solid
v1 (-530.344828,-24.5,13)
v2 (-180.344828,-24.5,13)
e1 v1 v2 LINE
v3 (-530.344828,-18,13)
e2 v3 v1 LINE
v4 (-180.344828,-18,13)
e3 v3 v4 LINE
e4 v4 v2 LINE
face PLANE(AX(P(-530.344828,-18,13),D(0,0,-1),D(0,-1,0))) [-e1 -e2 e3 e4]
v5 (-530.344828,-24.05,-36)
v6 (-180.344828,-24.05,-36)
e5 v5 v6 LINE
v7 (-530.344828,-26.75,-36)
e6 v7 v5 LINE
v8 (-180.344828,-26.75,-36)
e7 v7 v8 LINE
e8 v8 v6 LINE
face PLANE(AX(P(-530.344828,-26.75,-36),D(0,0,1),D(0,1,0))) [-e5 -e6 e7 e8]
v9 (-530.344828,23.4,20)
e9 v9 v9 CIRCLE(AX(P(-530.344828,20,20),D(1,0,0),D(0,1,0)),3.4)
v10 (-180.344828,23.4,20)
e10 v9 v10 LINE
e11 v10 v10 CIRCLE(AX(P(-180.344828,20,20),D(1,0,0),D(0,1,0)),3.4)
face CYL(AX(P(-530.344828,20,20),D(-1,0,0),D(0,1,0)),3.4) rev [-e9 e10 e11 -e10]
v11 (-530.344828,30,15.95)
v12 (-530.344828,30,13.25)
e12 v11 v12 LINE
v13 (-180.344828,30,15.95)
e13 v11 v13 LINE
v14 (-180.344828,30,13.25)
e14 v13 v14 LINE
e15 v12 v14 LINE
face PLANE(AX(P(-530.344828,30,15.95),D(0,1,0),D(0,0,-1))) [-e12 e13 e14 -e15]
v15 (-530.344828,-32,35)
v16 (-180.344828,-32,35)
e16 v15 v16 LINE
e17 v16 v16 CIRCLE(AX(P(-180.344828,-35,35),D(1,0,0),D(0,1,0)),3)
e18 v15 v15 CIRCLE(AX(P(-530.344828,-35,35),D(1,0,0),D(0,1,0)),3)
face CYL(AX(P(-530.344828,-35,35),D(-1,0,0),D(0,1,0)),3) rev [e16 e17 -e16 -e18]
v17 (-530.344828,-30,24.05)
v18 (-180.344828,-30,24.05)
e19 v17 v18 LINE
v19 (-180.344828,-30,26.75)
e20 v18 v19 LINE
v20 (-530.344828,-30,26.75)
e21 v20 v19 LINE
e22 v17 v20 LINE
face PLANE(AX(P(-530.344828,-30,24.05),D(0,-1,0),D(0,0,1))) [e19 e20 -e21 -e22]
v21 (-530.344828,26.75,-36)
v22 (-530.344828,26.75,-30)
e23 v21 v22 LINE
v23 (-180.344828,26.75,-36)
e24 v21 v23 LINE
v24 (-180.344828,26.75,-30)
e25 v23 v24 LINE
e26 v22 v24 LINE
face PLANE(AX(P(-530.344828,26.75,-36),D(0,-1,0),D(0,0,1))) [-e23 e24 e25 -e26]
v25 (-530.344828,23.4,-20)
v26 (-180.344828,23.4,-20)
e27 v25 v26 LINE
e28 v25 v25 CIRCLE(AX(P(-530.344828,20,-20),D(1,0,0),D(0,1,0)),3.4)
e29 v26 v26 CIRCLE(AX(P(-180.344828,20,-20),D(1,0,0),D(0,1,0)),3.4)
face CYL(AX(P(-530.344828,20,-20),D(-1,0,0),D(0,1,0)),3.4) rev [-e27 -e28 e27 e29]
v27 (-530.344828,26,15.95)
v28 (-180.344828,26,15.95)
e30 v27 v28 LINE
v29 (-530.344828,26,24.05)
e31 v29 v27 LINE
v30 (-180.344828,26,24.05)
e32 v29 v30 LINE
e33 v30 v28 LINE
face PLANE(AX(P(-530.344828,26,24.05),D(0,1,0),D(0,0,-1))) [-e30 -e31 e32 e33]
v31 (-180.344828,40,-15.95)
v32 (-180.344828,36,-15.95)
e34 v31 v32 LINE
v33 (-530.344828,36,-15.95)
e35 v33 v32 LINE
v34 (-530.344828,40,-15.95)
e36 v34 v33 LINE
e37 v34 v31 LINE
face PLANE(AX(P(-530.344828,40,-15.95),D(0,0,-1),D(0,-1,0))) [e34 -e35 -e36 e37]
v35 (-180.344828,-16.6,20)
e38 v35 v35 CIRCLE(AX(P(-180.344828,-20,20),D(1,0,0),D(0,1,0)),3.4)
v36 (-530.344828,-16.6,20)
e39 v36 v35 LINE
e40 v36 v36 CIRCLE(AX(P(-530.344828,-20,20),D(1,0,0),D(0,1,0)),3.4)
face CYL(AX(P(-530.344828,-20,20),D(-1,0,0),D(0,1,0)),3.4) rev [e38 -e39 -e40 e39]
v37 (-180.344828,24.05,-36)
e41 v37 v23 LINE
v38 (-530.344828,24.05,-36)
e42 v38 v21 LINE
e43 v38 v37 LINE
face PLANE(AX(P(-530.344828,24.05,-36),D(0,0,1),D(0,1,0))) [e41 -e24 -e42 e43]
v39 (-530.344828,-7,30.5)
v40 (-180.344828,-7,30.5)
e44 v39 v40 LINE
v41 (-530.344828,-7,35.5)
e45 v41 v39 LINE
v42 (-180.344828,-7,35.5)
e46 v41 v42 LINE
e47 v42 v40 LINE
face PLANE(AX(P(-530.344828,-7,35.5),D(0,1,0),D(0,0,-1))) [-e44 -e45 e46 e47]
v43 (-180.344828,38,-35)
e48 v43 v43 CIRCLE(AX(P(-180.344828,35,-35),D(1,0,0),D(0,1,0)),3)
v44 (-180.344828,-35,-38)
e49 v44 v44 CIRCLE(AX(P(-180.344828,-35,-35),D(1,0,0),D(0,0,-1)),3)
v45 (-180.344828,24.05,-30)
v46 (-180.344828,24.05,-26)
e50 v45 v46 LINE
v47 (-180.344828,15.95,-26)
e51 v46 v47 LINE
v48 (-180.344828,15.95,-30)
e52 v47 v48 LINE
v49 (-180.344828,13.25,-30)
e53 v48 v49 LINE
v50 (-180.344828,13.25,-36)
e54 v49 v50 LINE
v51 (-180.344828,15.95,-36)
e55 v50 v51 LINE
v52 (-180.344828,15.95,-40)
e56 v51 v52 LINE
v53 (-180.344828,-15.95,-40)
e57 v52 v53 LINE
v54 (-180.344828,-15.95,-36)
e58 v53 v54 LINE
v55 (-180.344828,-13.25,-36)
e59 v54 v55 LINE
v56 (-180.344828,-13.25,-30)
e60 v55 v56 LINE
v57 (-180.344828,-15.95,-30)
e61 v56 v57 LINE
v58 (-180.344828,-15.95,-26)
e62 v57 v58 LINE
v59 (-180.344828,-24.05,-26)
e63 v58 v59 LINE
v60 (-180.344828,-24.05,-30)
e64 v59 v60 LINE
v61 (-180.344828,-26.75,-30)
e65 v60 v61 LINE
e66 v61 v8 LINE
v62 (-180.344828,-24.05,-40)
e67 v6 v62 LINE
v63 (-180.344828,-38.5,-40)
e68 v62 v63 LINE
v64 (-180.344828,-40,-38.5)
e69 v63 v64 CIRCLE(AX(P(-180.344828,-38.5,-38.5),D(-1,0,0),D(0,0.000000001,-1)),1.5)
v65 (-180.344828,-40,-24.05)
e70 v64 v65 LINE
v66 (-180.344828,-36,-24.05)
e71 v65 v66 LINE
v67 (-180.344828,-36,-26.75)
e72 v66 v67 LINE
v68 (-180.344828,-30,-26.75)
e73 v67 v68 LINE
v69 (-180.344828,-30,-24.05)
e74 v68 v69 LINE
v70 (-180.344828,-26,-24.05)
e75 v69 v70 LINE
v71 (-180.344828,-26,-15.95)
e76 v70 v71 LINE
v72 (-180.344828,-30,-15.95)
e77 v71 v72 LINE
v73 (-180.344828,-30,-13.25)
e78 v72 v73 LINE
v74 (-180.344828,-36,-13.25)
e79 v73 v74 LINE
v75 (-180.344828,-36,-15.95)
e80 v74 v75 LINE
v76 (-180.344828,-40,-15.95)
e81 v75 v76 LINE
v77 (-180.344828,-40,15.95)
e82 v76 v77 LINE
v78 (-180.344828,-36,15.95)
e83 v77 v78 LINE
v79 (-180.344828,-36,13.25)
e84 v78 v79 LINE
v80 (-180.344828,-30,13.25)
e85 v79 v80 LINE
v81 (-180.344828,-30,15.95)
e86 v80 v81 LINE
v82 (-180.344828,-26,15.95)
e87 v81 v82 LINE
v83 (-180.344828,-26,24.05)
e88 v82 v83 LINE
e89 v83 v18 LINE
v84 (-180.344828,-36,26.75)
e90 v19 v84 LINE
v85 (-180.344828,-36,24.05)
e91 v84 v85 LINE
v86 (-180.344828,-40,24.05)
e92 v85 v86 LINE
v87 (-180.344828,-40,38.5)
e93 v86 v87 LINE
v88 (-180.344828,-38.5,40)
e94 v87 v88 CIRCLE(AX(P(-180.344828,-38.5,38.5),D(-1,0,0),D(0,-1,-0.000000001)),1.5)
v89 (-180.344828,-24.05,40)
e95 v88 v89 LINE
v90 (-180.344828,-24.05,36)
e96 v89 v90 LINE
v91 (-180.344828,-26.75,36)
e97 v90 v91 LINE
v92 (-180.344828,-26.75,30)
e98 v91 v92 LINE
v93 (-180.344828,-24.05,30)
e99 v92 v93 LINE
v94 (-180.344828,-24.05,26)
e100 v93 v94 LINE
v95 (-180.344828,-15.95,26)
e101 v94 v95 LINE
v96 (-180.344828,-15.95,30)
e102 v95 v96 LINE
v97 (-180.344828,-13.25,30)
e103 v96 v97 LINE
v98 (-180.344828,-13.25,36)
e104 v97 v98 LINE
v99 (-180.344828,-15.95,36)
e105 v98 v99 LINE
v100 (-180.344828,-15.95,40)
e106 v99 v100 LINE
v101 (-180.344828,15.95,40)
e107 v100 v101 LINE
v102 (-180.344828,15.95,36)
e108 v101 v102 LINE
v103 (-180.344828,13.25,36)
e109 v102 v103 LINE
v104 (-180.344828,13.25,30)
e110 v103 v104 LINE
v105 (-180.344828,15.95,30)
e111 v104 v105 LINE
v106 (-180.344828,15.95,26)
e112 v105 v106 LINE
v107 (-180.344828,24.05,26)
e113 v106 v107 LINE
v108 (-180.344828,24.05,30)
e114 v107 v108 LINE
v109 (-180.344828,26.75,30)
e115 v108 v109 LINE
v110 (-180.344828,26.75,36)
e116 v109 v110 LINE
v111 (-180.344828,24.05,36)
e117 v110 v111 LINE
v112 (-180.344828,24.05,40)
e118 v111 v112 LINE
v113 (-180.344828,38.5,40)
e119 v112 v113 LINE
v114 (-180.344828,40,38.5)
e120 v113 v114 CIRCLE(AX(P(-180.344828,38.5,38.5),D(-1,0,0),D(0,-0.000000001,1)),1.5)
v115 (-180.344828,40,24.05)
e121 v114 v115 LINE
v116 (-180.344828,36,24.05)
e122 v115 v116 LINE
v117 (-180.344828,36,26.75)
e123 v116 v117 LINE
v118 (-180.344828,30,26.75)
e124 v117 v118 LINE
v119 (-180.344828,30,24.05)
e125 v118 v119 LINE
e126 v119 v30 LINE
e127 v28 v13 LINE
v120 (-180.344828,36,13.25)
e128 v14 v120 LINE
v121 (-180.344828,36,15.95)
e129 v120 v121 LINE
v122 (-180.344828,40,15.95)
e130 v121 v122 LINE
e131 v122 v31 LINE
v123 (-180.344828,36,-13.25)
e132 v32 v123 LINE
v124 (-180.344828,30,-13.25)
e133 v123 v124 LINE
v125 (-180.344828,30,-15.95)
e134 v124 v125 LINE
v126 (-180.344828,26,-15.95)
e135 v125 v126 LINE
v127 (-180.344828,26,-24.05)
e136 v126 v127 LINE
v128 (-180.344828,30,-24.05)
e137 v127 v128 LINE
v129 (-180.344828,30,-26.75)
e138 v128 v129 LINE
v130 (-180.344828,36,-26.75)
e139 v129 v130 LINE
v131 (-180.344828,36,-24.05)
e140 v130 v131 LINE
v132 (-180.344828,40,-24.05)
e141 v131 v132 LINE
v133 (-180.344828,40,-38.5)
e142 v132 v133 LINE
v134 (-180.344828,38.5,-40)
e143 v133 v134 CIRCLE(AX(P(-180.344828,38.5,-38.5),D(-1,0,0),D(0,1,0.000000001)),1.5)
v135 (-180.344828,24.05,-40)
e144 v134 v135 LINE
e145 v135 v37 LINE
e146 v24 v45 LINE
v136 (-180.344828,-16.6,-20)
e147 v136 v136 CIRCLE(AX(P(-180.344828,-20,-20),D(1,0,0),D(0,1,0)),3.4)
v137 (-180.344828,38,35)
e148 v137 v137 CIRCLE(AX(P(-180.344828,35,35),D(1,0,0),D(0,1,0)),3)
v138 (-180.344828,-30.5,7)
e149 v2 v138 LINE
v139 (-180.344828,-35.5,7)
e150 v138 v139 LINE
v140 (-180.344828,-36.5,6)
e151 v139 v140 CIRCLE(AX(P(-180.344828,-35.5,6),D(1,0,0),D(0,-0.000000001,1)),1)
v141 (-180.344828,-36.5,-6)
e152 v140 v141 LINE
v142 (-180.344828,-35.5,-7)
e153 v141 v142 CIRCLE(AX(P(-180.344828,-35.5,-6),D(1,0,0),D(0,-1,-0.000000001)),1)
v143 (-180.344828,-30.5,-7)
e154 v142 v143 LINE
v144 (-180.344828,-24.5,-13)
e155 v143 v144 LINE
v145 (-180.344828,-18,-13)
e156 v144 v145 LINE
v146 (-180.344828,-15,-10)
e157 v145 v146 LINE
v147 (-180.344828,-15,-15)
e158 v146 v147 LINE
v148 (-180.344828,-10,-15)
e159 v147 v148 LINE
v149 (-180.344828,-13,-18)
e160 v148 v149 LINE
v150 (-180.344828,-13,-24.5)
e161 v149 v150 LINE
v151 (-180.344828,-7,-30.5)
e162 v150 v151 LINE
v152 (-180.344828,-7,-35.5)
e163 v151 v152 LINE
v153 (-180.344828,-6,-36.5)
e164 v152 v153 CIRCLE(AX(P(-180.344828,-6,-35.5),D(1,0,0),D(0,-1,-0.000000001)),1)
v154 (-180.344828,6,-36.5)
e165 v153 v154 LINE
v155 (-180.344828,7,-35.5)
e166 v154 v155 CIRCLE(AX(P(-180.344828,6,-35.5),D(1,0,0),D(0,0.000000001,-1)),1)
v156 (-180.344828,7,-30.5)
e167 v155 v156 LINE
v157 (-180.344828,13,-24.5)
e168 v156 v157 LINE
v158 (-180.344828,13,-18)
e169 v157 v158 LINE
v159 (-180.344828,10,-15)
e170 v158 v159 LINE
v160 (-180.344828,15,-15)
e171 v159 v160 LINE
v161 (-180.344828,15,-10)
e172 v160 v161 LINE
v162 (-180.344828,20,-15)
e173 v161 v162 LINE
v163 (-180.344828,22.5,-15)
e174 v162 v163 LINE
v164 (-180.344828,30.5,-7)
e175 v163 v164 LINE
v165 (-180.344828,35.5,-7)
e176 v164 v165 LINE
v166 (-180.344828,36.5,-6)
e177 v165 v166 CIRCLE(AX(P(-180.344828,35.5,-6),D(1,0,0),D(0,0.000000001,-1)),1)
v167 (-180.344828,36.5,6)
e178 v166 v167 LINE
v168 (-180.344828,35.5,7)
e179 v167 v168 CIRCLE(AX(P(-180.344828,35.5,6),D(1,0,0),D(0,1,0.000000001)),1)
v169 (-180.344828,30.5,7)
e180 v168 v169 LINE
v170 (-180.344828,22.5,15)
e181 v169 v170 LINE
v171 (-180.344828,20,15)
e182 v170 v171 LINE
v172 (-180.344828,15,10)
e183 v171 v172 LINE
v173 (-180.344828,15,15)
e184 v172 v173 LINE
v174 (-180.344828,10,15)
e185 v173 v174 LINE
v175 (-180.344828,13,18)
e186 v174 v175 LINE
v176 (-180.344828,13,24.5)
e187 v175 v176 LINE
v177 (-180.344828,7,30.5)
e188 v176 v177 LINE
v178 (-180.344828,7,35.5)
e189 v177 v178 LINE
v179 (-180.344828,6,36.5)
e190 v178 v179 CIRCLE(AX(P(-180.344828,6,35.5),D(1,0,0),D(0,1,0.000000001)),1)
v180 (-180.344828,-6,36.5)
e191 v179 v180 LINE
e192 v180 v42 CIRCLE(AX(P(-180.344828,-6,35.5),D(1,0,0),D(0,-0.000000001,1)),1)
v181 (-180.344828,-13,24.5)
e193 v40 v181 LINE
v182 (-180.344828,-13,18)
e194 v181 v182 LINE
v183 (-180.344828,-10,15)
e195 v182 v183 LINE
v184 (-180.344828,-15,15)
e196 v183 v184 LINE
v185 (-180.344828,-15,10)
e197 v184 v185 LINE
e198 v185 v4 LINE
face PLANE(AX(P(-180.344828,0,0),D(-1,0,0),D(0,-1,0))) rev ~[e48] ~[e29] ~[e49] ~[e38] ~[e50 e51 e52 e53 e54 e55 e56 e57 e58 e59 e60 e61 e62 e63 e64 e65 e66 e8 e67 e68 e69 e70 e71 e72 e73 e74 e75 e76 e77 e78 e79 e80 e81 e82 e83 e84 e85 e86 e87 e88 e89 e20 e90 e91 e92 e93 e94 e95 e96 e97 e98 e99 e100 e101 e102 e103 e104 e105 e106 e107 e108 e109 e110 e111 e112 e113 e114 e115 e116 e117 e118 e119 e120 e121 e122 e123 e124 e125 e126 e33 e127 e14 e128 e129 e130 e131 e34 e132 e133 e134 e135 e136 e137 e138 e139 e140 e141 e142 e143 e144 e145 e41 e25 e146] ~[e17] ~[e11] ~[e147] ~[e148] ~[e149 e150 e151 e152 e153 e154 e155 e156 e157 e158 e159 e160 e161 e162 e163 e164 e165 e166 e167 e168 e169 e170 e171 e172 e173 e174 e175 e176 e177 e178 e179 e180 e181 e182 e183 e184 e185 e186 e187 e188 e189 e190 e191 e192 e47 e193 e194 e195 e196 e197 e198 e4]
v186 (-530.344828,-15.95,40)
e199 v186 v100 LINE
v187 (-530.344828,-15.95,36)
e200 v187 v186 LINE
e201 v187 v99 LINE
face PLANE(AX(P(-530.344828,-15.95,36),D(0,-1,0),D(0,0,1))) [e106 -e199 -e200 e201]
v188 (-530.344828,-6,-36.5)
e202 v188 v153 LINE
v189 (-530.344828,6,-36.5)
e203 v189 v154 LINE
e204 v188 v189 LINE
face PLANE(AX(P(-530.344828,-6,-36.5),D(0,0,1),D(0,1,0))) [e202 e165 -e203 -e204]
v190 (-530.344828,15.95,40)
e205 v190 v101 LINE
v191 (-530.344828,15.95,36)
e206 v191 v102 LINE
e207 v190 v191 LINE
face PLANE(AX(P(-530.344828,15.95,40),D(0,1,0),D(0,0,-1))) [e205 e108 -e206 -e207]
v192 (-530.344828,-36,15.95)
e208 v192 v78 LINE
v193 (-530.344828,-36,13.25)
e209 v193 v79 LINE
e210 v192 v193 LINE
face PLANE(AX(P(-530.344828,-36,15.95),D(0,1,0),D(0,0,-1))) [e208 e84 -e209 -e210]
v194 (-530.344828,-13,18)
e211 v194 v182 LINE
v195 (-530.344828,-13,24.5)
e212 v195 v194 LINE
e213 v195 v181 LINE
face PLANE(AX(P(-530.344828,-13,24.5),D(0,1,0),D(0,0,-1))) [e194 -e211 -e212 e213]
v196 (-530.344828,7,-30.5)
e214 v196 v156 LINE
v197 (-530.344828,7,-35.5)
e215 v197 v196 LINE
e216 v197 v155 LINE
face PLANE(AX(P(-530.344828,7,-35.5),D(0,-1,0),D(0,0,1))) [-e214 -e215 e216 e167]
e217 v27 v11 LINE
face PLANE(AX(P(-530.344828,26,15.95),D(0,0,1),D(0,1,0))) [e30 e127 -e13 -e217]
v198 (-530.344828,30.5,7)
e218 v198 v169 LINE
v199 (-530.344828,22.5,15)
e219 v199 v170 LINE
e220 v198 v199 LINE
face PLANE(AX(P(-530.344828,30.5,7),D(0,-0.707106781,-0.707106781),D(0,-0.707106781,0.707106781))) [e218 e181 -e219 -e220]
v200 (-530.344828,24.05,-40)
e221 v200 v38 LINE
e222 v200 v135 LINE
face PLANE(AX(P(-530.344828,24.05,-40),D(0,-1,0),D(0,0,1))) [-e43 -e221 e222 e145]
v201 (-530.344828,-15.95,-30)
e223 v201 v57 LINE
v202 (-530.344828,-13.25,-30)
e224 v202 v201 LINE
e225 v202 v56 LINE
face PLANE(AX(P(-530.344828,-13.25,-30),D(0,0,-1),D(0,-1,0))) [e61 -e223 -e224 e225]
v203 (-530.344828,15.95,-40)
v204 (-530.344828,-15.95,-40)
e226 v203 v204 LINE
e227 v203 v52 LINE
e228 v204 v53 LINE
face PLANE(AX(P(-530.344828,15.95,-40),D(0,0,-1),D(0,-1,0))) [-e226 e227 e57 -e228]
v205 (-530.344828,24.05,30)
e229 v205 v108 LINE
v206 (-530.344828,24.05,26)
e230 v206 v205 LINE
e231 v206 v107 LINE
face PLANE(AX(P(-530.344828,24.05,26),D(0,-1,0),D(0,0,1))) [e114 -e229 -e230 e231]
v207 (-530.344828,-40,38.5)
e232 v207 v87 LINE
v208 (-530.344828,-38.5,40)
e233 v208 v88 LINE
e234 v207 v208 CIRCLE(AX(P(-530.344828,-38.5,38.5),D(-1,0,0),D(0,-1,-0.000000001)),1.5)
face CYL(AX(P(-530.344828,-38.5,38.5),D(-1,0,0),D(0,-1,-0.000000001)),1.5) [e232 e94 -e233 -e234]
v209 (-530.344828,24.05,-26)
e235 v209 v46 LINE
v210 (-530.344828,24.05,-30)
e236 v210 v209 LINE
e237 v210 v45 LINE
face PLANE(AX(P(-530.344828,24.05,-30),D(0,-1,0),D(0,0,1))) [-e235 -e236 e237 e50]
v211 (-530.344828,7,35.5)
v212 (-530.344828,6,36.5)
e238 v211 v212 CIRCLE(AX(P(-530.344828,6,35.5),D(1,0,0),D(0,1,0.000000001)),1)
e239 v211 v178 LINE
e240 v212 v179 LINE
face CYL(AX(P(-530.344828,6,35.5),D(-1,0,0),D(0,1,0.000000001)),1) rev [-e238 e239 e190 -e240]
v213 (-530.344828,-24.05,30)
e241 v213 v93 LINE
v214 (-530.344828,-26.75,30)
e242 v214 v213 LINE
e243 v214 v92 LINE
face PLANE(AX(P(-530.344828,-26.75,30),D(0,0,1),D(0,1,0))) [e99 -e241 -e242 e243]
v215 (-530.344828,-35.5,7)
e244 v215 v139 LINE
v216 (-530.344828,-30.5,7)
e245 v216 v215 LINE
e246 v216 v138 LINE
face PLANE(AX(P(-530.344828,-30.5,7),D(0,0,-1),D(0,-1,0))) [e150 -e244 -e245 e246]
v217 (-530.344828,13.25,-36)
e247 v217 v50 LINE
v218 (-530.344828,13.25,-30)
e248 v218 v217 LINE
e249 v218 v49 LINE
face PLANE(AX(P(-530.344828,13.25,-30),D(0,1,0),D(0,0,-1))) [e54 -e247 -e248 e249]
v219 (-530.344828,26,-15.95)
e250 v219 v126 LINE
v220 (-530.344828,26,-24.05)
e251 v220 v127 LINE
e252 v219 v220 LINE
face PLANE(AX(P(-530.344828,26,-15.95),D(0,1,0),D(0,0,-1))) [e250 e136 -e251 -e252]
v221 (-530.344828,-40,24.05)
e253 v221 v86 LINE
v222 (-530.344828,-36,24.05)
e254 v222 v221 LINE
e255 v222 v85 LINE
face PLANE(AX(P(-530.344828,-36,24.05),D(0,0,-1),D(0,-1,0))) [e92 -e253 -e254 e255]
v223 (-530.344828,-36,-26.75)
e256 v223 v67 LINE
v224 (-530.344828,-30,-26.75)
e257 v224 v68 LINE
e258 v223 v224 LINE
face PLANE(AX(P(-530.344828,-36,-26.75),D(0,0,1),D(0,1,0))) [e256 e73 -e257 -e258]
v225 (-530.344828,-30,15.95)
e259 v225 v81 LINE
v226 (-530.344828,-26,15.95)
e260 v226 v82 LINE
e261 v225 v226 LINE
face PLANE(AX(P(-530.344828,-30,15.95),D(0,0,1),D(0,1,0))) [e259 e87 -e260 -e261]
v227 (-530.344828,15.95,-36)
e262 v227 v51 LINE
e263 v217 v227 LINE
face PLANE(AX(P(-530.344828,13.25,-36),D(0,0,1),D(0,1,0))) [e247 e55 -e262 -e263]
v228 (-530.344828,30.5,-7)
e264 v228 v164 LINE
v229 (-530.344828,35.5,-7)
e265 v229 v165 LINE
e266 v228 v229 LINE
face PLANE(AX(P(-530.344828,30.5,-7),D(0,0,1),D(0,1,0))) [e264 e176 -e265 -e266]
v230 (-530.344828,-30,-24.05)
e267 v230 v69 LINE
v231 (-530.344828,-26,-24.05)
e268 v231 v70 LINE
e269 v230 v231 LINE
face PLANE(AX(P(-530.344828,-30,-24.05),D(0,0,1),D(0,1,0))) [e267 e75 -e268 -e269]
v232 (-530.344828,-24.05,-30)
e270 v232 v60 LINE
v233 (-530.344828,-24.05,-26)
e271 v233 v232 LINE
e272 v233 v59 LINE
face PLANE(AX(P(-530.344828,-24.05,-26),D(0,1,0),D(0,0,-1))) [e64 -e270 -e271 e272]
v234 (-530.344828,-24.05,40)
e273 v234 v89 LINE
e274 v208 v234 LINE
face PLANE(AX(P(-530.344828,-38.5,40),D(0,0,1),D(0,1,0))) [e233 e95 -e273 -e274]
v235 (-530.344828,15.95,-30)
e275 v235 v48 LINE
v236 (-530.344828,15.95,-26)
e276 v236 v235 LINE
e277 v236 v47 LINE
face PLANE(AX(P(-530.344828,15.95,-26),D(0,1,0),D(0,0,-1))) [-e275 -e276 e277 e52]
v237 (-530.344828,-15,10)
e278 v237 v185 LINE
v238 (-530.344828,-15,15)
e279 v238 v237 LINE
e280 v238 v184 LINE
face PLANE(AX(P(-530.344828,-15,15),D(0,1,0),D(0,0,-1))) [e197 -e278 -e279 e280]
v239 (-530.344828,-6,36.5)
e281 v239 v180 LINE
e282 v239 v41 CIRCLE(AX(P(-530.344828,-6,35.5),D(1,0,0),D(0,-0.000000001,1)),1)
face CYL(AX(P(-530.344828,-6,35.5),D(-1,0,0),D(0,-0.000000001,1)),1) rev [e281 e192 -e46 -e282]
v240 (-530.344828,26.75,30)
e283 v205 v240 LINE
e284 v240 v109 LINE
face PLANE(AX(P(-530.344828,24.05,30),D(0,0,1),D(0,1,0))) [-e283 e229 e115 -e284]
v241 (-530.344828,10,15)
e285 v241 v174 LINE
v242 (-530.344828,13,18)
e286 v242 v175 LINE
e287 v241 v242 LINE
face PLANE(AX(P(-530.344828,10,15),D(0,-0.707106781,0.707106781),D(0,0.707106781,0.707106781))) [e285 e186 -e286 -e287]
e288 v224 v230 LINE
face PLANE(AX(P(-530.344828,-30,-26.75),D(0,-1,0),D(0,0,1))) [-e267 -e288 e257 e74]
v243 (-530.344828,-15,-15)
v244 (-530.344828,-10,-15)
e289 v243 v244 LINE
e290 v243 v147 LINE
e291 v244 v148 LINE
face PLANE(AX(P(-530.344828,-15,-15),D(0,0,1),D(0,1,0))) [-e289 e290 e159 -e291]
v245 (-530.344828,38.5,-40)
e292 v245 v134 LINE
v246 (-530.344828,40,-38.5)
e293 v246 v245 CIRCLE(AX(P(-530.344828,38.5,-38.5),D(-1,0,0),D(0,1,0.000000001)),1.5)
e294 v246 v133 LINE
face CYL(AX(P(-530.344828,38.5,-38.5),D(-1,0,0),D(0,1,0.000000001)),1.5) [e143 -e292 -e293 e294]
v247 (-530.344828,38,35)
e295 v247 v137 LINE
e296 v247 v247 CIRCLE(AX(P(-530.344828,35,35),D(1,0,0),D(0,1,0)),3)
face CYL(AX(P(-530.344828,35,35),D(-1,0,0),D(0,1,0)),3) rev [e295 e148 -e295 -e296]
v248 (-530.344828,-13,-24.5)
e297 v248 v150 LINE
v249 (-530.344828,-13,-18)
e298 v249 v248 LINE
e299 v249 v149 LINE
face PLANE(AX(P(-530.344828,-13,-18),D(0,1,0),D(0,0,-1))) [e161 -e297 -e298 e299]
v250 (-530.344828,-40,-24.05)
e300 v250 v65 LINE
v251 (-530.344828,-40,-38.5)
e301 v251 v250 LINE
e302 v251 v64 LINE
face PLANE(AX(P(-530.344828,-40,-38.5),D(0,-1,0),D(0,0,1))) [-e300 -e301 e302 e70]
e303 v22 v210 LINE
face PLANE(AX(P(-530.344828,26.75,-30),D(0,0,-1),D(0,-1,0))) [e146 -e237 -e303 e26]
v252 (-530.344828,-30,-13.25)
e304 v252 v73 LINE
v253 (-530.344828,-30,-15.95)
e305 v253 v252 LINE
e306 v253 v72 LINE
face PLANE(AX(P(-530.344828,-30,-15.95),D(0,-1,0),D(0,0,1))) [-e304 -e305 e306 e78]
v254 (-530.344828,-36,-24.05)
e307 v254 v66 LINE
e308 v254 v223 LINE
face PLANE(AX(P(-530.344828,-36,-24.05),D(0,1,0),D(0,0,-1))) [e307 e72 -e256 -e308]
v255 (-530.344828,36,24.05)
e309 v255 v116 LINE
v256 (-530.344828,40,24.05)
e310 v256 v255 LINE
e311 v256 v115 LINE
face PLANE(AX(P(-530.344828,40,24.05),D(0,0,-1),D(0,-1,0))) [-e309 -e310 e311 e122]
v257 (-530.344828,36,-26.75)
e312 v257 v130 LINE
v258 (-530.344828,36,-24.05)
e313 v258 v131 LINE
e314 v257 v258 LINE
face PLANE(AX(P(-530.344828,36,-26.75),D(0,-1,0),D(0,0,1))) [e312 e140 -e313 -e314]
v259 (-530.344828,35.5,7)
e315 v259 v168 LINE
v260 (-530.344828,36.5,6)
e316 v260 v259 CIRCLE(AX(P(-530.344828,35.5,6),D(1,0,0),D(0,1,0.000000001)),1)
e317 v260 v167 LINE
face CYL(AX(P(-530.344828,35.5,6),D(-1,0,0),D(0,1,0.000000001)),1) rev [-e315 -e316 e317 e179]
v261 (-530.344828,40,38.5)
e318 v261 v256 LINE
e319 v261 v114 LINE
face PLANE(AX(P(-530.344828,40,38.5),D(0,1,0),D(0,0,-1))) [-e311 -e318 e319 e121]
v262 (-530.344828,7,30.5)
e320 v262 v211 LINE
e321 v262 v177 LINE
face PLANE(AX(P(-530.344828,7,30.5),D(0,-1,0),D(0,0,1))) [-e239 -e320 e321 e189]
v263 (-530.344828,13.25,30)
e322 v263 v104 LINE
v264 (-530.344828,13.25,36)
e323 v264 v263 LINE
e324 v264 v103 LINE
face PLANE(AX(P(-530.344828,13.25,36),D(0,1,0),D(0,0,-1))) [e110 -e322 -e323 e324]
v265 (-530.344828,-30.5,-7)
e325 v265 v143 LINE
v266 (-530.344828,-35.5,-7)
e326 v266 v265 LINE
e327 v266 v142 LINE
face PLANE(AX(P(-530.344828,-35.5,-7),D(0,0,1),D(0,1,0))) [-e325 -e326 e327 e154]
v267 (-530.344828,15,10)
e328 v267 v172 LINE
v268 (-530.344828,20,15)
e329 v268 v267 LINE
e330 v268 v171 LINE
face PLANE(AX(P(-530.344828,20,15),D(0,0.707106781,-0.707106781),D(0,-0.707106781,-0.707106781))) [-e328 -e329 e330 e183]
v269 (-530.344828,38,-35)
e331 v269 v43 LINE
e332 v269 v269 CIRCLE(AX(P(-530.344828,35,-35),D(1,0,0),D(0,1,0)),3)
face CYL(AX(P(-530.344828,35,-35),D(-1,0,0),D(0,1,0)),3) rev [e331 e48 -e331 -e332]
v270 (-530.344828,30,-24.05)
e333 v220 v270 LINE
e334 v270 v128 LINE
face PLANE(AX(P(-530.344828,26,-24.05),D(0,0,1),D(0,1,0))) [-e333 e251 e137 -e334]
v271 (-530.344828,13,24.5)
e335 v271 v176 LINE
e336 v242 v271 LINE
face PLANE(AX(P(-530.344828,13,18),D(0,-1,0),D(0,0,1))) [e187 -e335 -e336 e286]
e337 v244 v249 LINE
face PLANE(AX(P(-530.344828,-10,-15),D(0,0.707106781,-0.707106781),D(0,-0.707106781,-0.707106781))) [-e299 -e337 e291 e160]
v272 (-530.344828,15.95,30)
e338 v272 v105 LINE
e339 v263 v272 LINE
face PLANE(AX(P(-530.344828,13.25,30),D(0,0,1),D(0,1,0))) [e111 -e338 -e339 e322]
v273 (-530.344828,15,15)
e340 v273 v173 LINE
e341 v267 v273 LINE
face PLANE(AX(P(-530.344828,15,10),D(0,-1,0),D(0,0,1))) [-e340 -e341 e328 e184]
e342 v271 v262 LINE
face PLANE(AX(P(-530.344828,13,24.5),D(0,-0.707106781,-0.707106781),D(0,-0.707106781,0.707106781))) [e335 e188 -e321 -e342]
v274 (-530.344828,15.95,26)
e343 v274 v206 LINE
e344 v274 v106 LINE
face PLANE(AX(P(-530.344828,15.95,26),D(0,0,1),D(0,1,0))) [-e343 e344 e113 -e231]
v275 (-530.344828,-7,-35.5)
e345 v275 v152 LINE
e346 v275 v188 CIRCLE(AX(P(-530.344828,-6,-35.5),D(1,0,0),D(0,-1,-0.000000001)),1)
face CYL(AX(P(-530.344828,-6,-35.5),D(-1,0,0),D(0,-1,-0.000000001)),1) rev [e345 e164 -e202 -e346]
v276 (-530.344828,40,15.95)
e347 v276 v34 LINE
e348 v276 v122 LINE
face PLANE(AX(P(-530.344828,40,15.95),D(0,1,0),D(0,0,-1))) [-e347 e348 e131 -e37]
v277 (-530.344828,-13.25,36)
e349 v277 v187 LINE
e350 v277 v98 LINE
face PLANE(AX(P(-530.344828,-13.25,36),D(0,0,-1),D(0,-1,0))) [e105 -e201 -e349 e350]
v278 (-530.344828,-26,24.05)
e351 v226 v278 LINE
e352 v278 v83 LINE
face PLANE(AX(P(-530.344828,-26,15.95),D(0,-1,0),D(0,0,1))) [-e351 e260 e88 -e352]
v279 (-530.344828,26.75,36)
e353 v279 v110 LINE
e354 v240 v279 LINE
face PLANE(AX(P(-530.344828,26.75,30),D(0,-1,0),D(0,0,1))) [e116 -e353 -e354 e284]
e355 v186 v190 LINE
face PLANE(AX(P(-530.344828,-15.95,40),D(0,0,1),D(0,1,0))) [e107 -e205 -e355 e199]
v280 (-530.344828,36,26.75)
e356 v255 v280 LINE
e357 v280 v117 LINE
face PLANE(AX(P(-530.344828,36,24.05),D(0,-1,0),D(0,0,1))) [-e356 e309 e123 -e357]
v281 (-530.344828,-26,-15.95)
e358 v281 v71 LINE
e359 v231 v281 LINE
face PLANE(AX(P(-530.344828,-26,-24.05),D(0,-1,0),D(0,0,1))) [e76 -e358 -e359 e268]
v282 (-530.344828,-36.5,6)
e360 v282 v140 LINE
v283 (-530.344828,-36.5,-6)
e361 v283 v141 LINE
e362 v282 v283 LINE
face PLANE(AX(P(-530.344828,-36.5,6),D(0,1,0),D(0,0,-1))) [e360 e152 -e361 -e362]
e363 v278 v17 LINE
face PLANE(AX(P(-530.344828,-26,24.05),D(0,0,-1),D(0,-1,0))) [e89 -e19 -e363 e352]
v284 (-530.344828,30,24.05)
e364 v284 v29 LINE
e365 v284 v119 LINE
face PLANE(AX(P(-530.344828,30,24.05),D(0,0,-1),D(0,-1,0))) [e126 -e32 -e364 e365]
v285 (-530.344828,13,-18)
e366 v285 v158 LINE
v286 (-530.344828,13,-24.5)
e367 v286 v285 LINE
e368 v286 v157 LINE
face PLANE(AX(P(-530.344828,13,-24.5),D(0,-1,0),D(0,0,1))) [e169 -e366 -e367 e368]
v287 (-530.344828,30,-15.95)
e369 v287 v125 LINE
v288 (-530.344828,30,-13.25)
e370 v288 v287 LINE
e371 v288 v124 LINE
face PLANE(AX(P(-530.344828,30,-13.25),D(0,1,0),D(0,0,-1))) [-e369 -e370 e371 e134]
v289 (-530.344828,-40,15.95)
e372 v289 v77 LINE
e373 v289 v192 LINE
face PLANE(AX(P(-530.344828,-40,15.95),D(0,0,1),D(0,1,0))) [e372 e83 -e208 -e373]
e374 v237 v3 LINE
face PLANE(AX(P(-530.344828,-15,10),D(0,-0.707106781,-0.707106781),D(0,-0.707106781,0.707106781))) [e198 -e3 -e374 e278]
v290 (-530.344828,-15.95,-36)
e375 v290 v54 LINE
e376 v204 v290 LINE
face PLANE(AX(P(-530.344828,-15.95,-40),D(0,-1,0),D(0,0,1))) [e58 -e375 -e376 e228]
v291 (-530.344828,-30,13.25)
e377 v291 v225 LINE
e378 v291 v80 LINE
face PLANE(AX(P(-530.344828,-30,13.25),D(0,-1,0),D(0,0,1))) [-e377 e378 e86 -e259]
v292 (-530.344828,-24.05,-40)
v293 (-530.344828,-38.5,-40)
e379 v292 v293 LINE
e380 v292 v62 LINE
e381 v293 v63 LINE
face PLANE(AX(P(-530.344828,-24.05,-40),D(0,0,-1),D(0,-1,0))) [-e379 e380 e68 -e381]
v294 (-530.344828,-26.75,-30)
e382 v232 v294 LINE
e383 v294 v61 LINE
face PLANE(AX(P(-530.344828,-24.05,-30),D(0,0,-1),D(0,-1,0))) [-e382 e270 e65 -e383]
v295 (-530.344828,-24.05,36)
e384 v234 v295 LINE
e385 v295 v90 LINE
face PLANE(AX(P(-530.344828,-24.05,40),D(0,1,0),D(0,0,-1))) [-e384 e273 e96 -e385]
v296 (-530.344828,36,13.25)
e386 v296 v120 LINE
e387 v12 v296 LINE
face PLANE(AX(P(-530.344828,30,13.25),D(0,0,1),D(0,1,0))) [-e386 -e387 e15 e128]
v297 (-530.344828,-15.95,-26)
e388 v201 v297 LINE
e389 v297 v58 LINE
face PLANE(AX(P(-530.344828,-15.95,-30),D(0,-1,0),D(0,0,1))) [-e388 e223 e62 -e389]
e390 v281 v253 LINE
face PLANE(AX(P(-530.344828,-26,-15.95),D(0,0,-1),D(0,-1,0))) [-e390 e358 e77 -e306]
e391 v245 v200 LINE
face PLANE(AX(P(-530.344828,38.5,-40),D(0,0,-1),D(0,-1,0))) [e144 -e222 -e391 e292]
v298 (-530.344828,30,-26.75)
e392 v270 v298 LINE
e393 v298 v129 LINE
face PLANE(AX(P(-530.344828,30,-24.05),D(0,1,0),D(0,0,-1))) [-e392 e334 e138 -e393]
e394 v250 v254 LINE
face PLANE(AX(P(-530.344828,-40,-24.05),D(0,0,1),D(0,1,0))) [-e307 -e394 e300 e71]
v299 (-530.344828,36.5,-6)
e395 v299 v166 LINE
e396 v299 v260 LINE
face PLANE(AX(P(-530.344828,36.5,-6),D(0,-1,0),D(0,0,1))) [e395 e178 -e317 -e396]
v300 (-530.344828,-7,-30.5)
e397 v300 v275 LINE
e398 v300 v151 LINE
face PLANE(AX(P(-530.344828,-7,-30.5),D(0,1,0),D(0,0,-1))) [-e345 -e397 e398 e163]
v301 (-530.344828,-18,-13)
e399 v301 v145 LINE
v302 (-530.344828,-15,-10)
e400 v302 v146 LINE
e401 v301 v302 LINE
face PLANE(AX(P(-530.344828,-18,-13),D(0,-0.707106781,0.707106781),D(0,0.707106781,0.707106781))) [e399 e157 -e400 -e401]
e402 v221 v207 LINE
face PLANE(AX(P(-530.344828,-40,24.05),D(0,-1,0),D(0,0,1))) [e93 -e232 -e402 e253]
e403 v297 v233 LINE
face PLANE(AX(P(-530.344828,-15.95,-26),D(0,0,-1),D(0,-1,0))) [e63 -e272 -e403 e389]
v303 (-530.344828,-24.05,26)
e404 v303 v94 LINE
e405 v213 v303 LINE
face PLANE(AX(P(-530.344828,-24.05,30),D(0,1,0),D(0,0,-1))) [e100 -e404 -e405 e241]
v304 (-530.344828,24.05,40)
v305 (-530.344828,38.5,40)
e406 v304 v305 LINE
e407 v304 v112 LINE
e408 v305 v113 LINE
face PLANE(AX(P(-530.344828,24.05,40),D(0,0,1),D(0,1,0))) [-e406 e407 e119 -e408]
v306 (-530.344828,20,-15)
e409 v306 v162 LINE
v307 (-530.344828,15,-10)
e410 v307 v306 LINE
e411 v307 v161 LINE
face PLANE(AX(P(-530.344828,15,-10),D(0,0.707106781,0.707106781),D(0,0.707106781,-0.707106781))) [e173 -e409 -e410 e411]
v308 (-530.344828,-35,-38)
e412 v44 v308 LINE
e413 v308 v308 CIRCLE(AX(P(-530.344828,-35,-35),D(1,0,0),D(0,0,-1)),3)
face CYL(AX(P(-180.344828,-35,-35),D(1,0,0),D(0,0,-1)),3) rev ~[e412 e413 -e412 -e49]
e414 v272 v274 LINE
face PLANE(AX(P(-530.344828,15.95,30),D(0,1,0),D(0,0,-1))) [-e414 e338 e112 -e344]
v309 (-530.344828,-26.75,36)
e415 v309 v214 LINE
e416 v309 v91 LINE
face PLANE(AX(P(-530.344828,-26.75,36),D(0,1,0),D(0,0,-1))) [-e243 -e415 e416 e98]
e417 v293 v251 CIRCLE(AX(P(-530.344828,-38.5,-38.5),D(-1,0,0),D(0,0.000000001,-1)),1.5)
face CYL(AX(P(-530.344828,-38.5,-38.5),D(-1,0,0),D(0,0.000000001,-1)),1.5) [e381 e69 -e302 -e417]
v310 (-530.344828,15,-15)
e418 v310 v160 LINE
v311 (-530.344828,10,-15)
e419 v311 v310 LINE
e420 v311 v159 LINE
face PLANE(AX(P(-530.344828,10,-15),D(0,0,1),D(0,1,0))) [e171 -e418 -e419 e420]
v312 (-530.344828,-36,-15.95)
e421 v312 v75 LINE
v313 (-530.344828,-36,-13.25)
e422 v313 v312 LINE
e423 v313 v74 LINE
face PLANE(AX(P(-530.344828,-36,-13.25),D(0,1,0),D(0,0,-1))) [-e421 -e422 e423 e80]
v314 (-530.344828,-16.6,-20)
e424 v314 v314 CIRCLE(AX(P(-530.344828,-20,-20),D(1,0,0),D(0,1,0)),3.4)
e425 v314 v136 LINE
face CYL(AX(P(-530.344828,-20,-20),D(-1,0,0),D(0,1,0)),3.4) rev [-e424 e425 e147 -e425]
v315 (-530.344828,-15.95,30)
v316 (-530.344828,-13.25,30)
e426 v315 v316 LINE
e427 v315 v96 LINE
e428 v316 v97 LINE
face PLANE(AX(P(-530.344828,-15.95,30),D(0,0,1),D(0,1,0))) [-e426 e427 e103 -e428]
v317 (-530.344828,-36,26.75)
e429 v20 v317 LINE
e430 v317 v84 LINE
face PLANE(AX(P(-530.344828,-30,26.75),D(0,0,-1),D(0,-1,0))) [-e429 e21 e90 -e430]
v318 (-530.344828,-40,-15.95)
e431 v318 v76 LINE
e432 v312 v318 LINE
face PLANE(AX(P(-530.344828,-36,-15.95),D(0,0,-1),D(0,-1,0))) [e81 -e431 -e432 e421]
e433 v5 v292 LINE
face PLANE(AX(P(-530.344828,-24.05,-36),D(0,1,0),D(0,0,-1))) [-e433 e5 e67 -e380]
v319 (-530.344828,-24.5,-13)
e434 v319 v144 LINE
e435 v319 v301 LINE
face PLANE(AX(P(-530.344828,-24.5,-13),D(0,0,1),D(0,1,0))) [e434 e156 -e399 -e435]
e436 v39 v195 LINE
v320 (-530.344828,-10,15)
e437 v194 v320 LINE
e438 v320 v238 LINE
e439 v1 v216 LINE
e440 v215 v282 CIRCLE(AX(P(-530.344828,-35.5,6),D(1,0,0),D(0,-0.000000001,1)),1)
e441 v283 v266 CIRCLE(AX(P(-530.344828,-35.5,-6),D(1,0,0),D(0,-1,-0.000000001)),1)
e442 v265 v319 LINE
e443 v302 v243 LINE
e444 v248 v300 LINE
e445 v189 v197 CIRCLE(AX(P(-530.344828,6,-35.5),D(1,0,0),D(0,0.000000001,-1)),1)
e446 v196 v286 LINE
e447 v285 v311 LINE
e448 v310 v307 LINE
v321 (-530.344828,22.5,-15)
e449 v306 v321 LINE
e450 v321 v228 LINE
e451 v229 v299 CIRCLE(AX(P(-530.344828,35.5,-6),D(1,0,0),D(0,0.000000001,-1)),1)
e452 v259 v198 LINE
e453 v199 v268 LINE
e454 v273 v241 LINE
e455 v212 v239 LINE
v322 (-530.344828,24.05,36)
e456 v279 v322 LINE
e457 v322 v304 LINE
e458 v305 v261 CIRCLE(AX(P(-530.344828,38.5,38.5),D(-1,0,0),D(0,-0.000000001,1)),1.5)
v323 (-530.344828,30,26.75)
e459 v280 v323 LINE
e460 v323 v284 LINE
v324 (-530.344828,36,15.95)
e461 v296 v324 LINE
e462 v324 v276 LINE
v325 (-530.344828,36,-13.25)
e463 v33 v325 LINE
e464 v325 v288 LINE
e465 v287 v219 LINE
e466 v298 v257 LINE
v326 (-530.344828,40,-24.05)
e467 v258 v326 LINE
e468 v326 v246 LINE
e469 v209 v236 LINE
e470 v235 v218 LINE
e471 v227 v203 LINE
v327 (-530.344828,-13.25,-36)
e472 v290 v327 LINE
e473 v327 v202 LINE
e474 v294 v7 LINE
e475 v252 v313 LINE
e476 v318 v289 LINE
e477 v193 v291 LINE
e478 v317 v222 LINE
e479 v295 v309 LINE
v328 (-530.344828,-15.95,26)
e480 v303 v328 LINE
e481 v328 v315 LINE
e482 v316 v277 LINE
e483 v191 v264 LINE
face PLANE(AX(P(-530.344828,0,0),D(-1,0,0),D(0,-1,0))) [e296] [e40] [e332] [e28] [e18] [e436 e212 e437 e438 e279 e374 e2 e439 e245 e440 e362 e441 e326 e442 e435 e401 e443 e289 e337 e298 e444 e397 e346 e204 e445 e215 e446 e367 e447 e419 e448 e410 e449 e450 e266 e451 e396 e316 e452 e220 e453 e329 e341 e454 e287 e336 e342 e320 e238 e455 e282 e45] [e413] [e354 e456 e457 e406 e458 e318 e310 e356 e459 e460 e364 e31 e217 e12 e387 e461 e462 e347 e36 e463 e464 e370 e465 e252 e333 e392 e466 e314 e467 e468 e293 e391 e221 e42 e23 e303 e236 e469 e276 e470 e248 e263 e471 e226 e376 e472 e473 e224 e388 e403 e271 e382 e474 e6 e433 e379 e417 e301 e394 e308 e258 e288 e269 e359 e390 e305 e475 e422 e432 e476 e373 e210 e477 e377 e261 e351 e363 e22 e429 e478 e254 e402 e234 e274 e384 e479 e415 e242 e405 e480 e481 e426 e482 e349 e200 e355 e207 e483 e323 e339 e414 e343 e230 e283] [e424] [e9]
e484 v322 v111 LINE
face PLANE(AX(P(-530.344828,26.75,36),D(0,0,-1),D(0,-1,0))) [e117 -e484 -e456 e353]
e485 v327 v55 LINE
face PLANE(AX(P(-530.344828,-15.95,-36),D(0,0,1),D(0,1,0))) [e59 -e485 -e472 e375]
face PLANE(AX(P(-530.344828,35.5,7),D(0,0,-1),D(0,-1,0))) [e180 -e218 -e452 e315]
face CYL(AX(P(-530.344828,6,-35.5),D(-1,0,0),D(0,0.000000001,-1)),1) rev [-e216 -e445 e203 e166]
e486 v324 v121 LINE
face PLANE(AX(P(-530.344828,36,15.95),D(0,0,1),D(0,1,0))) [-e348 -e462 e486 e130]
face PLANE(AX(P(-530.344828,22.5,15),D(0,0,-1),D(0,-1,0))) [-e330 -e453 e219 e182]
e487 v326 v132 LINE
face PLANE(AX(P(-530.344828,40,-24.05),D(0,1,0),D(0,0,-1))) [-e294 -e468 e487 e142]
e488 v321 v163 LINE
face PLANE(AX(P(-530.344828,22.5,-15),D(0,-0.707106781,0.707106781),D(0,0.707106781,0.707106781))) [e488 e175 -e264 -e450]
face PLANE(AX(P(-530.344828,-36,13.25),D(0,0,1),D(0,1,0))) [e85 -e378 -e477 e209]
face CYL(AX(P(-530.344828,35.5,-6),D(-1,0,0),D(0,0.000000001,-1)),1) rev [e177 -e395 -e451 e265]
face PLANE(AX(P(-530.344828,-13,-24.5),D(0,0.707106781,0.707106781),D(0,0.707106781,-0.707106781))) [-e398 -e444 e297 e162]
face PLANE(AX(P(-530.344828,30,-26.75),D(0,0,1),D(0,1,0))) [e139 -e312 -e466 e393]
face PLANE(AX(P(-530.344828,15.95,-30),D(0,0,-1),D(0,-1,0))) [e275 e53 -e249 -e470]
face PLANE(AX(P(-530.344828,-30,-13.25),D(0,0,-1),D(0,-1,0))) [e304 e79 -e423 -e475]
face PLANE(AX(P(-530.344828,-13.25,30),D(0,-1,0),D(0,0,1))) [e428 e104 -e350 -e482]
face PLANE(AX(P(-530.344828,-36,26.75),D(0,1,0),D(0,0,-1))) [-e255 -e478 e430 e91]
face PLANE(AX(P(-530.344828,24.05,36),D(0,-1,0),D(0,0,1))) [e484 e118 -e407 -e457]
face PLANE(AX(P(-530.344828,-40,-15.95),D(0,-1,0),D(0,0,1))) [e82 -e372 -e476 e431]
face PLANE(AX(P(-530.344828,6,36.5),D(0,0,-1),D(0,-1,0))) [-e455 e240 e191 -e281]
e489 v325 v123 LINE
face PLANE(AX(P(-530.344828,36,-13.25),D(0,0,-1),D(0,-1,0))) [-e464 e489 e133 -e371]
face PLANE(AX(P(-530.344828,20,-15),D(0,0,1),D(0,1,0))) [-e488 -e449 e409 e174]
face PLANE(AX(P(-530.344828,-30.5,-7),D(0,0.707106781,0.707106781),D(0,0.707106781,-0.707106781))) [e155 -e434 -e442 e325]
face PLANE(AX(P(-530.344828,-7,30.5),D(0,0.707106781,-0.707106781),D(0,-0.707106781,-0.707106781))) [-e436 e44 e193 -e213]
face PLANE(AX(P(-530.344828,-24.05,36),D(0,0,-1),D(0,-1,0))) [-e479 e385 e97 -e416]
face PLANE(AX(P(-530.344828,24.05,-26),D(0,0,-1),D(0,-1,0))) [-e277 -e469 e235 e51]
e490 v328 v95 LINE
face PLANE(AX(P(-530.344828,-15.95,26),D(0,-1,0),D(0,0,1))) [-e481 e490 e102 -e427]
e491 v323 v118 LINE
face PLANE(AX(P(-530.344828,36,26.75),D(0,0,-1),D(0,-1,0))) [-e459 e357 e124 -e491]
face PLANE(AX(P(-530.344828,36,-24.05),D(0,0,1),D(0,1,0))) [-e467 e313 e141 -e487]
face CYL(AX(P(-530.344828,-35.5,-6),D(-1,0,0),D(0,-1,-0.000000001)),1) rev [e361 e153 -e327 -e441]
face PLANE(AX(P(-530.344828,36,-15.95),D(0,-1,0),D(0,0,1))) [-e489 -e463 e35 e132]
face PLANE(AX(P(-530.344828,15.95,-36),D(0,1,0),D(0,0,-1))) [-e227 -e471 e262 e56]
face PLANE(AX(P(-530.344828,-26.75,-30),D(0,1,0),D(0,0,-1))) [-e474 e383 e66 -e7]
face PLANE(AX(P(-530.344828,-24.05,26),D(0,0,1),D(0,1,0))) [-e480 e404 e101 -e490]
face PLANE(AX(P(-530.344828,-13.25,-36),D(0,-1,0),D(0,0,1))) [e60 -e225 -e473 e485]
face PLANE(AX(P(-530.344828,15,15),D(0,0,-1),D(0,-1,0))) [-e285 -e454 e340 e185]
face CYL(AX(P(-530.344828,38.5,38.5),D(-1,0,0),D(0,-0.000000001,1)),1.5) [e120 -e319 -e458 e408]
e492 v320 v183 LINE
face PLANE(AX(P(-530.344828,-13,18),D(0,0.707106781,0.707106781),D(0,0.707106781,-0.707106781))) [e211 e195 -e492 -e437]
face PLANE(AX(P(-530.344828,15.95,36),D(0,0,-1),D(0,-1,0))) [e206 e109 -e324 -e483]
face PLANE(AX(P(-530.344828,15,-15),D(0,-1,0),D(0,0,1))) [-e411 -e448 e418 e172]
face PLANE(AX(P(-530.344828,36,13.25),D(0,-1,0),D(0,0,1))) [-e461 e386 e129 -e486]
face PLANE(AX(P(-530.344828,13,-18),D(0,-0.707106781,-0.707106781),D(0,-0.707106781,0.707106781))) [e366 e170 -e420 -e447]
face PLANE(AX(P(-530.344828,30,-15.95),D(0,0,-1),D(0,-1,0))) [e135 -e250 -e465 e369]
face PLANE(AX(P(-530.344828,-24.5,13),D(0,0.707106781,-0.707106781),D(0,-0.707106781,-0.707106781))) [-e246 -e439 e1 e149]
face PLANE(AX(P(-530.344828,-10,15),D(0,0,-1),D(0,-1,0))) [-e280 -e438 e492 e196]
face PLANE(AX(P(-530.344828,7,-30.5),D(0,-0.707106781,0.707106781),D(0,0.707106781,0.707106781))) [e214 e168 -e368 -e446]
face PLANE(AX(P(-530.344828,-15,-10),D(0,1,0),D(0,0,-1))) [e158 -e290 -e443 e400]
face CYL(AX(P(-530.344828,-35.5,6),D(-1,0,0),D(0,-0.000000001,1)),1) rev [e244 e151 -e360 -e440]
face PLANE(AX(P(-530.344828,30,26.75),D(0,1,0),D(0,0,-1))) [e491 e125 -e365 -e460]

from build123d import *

# Parameters (mm, degrees)
SKETCH1_R                                 = 3.4
SKETCH1_R_2                               = 3
ALUMINIUM_PROFILE_80_X_80G_X_R1_5_1_DEPTH = 350
SKETCH10_R                                = 3
CUT_EXTRUDE1_DEPTH                        = 355.541958025


with BuildPart() as part:
    # Sketch1 → Aluminium profile 80 X 80G X R1.5(1) (new body)
    with BuildSketch(Plane.YZ.offset(-530.344827586)):
        with BuildLine():
            Line((-24.05, 40), (-24.05, 36))
            Line((-24.05, 36), (-26.75, 36))
            Line((-26.75, 36), (-26.75, 30))
            Line((-26.75, 30), (-24.05, 30))
            Line((-24.05, 30), (-24.05, 26))
            Line((-24.05, 26), (-15.95, 26))
            Line((-15.95, 26), (-15.95, 30))
            Line((-15.95, 30), (-13.25, 30))
            Line((-13.25, 30), (-13.25, 36))
            Line((-13.25, 36), (-15.95, 36))
            Line((-15.95, 36), (-15.95, 40))
            Line((-15.95, 40), (15.95, 40))
            Line((15.95, 40), (15.95, 36))
            Line((15.95, 36), (13.25, 36))
            Line((13.25, 36), (13.25, 30))
            Line((13.25, 30), (15.95, 30))
            Line((15.95, 30), (15.95, 26))
            Line((15.95, 26), (24.05, 26))
            Line((24.05, 26), (24.05, 30))
            Line((24.05, 30), (26.75, 30))
            Line((26.75, 30), (26.75, 36))
            Line((26.75, 36), (24.05, 36))
            Line((24.05, 36), (24.05, 40))
            Line((24.05, 40), (38.5, 40))
            ThreePointArc((38.5, 40), (39.560660172, 39.560660172), (40, 38.5))
            Line((40, 38.5), (40, 24.05))
            Line((40, 24.05), (36, 24.05))
            Line((36, 24.05), (36, 26.75))
            Line((36, 26.75), (30, 26.75))
            Line((30, 26.75), (30, 24.05))
            Line((30, 24.05), (26, 24.05))
            Line((26, 24.05), (26, 15.95))
            Line((26, 15.95), (30, 15.95))
            Line((30, 15.95), (30, 13.25))
            Line((30, 13.25), (36, 13.25))
            Line((36, 13.25), (36, 15.95))
            Line((36, 15.95), (40, 15.95))
            Line((40, 15.95), (40, -15.95))
            Line((40, -15.95), (36, -15.95))
            Line((36, -15.95), (36, -13.25))
            Line((36, -13.25), (30, -13.25))
            Line((30, -13.25), (30, -15.95))
            Line((30, -15.95), (26, -15.95))
            Line((26, -15.95), (26, -24.05))
            Line((26, -24.05), (30, -24.05))
            Line((30, -24.05), (30, -26.75))
            Line((30, -26.75), (36, -26.75))
            Line((36, -26.75), (36, -24.05))
            Line((36, -24.05), (40, -24.05))
            Line((40, -24.05), (40, -38.5))
            ThreePointArc((40, -38.5), (39.560660172, -39.560660172), (38.5, -40))
            Line((38.5, -40), (24.05, -40))
            Line((24.05, -40), (24.05, -36))
            Line((24.05, -36), (26.75, -36))
            Line((26.75, -36), (26.75, -30))
            Line((26.75, -30), (24.05, -30))
            Line((24.05, -30), (24.05, -26))
            Line((24.05, -26), (15.95, -26))
            Line((15.95, -26), (15.95, -30))
            Line((15.95, -30), (13.25, -30))
            Line((13.25, -30), (13.25, -36))
            Line((13.25, -36), (15.95, -36))
            Line((15.95, -36), (15.95, -40))
            Line((15.95, -40), (-15.95, -40))
            Line((-15.95, -40), (-15.95, -36))
            Line((-15.95, -36), (-13.25, -36))
            Line((-13.25, -36), (-13.25, -30))
            Line((-13.25, -30), (-15.95, -30))
            Line((-15.95, -30), (-15.95, -26))
            Line((-15.95, -26), (-24.05, -26))
            Line((-24.05, -26), (-24.05, -30))
            Line((-24.05, -30), (-26.75, -30))
            Line((-26.75, -30), (-26.75, -36))
            Line((-26.75, -36), (-24.05, -36))
            Line((-24.05, -36), (-24.05, -40))
            Line((-24.05, -40), (-38.5, -40))
            ThreePointArc((-38.5, -40), (-39.560660172, -39.560660172), (-40, -38.5))
            Line((-40, -38.5), (-40, -24.05))
            Line((-40, -24.05), (-36, -24.05))
            Line((-36, -24.05), (-36, -26.75))
            Line((-36, -26.75), (-30, -26.75))
            Line((-30, -26.75), (-30, -24.05))
            Line((-30, -24.05), (-26, -24.05))
            Line((-26, -24.05), (-26, -15.95))
            Line((-26, -15.95), (-30, -15.95))
            Line((-30, -15.95), (-30, -13.25))
            Line((-30, -13.25), (-36, -13.25))
            Line((-36, -13.25), (-36, -15.95))
            Line((-36, -15.95), (-40, -15.95))
            Line((-40, -15.95), (-40, 15.95))
            Line((-40, 15.95), (-36, 15.95))
            Line((-36, 15.95), (-36, 13.25))
            Line((-36, 13.25), (-30, 13.25))
            Line((-30, 13.25), (-30, 15.95))
            Line((-30, 15.95), (-26, 15.95))
            Line((-26, 15.95), (-26, 24.05))
            Line((-26, 24.05), (-30, 24.05))
            Line((-30, 24.05), (-30, 26.75))
            Line((-30, 26.75), (-36, 26.75))
            Line((-36, 26.75), (-36, 24.05))
            Line((-36, 24.05), (-40, 24.05))
            Line((-40, 24.05), (-40, 38.5))
            ThreePointArc((-40, 38.5), (-39.560660172, 39.560660172), (-38.5, 40))
            Line((-38.5, 40), (-24.05, 40))
        make_face()
        with Locations((-20, 20)):
            Circle(SKETCH1_R, mode=Mode.SUBTRACT)
        with Locations((20, 20)):
            Circle(SKETCH1_R, mode=Mode.SUBTRACT)
        with Locations((20, -20)):
            Circle(SKETCH1_R, mode=Mode.SUBTRACT)
        with Locations((-20, -20)):
            Circle(SKETCH1_R, mode=Mode.SUBTRACT)
        with Locations((-35, 35)):
            Circle(SKETCH1_R_2, mode=Mode.SUBTRACT)
        with Locations((35, 35)):
            Circle(SKETCH1_R_2, mode=Mode.SUBTRACT)
        with Locations((35, -35)):
            Circle(SKETCH1_R_2, mode=Mode.SUBTRACT)
        with BuildLine():
            Line((-13, 18), (-10, 15))
            Line((-10, 15), (-15, 15))
            Line((-15, 15), (-15, 10))
            Line((-15, 10), (-18, 13))
            Line((-18, 13), (-24.5, 13))
            Line((-24.5, 13), (-30.5, 7))
            Line((-30.5, 7), (-35.5, 7))
            ThreePointArc((-35.5, 7), (-36.207106781, 6.707106781), (-36.5, 6))
            Line((-36.5, 6), (-36.5, -6))
            ThreePointArc((-36.5, -6), (-36.207106781, -6.707106781), (-35.5, -7))
            Line((-35.5, -7), (-30.5, -7))
            Line((-30.5, -7), (-24.5, -13))
            Line((-24.5, -13), (-18, -13))
            Line((-18, -13), (-15, -10))
            Line((-15, -10), (-15, -15))
            Line((-15, -15), (-10, -15))
            Line((-10, -15), (-13, -18))
            Line((-13, -18), (-13, -24.5))
            Line((-13, -24.5), (-7, -30.5))
            Line((-7, -30.5), (-7, -35.5))
            ThreePointArc((-7, -35.5), (-6.707106781, -36.207106781), (-6, -36.5))
            Line((-6, -36.5), (6, -36.5))
            ThreePointArc((6, -36.5), (6.707106781, -36.207106781), (7, -35.5))
            Line((7, -35.5), (7, -30.5))
            Line((7, -30.5), (13, -24.5))
            Line((13, -24.5), (13, -18))
            Line((13, -18), (10, -15))
            Line((10, -15), (15, -15))
            Line((15, -15), (15, -10))
            Line((15, -10), (20, -15))
            Line((20, -15), (22.5, -15))
            Line((22.5, -15), (30.5, -7))
            Line((30.5, -7), (35.5, -7))
            ThreePointArc((35.5, -7), (36.207106781, -6.707106781), (36.5, -6))
            Line((36.5, -6), (36.5, 6))
            ThreePointArc((36.5, 6), (36.207106781, 6.707106781), (35.5, 7))
            Line((35.5, 7), (30.5, 7))
            Line((30.5, 7), (22.5, 15))
            Line((22.5, 15), (20, 15))
            Line((20, 15), (15, 10))
            Line((15, 10), (15, 15))
            Line((15, 15), (10, 15))
            Line((10, 15), (13, 18))
            Line((13, 18), (13, 24.5))
            Line((13, 24.5), (7, 30.5))
            Line((7, 30.5), (7, 35.5))
            ThreePointArc((7, 35.5), (6.707106781, 36.207106781), (6, 36.5))
            Line((6, 36.5), (-6, 36.5))
            ThreePointArc((-6, 36.5), (-6.707106781, 36.207106781), (-7, 35.5))
            Line((-7, 35.5), (-7, 30.5))
            Line((-7, 30.5), (-13, 24.5))
            Line((-13, 24.5), (-13, 18))
        make_face(mode=Mode.SUBTRACT)
    extrude(amount=ALUMINIUM_PROFILE_80_X_80G_X_R1_5_1_DEPTH)

    # Sketch10 → Cut-Extrude1 (cut, through all)
    with BuildSketch(Plane(origin=(-180.344827586, 0, 0), x_dir=(0, 0, -1), z_dir=(1, 0, 0))):
        with Locations((35, -35)):
            Circle(SKETCH10_R)
    extrude(amount=-CUT_EXTRUDE1_DEPTH, mode=Mode.SUBTRACT)


solid = part.part
